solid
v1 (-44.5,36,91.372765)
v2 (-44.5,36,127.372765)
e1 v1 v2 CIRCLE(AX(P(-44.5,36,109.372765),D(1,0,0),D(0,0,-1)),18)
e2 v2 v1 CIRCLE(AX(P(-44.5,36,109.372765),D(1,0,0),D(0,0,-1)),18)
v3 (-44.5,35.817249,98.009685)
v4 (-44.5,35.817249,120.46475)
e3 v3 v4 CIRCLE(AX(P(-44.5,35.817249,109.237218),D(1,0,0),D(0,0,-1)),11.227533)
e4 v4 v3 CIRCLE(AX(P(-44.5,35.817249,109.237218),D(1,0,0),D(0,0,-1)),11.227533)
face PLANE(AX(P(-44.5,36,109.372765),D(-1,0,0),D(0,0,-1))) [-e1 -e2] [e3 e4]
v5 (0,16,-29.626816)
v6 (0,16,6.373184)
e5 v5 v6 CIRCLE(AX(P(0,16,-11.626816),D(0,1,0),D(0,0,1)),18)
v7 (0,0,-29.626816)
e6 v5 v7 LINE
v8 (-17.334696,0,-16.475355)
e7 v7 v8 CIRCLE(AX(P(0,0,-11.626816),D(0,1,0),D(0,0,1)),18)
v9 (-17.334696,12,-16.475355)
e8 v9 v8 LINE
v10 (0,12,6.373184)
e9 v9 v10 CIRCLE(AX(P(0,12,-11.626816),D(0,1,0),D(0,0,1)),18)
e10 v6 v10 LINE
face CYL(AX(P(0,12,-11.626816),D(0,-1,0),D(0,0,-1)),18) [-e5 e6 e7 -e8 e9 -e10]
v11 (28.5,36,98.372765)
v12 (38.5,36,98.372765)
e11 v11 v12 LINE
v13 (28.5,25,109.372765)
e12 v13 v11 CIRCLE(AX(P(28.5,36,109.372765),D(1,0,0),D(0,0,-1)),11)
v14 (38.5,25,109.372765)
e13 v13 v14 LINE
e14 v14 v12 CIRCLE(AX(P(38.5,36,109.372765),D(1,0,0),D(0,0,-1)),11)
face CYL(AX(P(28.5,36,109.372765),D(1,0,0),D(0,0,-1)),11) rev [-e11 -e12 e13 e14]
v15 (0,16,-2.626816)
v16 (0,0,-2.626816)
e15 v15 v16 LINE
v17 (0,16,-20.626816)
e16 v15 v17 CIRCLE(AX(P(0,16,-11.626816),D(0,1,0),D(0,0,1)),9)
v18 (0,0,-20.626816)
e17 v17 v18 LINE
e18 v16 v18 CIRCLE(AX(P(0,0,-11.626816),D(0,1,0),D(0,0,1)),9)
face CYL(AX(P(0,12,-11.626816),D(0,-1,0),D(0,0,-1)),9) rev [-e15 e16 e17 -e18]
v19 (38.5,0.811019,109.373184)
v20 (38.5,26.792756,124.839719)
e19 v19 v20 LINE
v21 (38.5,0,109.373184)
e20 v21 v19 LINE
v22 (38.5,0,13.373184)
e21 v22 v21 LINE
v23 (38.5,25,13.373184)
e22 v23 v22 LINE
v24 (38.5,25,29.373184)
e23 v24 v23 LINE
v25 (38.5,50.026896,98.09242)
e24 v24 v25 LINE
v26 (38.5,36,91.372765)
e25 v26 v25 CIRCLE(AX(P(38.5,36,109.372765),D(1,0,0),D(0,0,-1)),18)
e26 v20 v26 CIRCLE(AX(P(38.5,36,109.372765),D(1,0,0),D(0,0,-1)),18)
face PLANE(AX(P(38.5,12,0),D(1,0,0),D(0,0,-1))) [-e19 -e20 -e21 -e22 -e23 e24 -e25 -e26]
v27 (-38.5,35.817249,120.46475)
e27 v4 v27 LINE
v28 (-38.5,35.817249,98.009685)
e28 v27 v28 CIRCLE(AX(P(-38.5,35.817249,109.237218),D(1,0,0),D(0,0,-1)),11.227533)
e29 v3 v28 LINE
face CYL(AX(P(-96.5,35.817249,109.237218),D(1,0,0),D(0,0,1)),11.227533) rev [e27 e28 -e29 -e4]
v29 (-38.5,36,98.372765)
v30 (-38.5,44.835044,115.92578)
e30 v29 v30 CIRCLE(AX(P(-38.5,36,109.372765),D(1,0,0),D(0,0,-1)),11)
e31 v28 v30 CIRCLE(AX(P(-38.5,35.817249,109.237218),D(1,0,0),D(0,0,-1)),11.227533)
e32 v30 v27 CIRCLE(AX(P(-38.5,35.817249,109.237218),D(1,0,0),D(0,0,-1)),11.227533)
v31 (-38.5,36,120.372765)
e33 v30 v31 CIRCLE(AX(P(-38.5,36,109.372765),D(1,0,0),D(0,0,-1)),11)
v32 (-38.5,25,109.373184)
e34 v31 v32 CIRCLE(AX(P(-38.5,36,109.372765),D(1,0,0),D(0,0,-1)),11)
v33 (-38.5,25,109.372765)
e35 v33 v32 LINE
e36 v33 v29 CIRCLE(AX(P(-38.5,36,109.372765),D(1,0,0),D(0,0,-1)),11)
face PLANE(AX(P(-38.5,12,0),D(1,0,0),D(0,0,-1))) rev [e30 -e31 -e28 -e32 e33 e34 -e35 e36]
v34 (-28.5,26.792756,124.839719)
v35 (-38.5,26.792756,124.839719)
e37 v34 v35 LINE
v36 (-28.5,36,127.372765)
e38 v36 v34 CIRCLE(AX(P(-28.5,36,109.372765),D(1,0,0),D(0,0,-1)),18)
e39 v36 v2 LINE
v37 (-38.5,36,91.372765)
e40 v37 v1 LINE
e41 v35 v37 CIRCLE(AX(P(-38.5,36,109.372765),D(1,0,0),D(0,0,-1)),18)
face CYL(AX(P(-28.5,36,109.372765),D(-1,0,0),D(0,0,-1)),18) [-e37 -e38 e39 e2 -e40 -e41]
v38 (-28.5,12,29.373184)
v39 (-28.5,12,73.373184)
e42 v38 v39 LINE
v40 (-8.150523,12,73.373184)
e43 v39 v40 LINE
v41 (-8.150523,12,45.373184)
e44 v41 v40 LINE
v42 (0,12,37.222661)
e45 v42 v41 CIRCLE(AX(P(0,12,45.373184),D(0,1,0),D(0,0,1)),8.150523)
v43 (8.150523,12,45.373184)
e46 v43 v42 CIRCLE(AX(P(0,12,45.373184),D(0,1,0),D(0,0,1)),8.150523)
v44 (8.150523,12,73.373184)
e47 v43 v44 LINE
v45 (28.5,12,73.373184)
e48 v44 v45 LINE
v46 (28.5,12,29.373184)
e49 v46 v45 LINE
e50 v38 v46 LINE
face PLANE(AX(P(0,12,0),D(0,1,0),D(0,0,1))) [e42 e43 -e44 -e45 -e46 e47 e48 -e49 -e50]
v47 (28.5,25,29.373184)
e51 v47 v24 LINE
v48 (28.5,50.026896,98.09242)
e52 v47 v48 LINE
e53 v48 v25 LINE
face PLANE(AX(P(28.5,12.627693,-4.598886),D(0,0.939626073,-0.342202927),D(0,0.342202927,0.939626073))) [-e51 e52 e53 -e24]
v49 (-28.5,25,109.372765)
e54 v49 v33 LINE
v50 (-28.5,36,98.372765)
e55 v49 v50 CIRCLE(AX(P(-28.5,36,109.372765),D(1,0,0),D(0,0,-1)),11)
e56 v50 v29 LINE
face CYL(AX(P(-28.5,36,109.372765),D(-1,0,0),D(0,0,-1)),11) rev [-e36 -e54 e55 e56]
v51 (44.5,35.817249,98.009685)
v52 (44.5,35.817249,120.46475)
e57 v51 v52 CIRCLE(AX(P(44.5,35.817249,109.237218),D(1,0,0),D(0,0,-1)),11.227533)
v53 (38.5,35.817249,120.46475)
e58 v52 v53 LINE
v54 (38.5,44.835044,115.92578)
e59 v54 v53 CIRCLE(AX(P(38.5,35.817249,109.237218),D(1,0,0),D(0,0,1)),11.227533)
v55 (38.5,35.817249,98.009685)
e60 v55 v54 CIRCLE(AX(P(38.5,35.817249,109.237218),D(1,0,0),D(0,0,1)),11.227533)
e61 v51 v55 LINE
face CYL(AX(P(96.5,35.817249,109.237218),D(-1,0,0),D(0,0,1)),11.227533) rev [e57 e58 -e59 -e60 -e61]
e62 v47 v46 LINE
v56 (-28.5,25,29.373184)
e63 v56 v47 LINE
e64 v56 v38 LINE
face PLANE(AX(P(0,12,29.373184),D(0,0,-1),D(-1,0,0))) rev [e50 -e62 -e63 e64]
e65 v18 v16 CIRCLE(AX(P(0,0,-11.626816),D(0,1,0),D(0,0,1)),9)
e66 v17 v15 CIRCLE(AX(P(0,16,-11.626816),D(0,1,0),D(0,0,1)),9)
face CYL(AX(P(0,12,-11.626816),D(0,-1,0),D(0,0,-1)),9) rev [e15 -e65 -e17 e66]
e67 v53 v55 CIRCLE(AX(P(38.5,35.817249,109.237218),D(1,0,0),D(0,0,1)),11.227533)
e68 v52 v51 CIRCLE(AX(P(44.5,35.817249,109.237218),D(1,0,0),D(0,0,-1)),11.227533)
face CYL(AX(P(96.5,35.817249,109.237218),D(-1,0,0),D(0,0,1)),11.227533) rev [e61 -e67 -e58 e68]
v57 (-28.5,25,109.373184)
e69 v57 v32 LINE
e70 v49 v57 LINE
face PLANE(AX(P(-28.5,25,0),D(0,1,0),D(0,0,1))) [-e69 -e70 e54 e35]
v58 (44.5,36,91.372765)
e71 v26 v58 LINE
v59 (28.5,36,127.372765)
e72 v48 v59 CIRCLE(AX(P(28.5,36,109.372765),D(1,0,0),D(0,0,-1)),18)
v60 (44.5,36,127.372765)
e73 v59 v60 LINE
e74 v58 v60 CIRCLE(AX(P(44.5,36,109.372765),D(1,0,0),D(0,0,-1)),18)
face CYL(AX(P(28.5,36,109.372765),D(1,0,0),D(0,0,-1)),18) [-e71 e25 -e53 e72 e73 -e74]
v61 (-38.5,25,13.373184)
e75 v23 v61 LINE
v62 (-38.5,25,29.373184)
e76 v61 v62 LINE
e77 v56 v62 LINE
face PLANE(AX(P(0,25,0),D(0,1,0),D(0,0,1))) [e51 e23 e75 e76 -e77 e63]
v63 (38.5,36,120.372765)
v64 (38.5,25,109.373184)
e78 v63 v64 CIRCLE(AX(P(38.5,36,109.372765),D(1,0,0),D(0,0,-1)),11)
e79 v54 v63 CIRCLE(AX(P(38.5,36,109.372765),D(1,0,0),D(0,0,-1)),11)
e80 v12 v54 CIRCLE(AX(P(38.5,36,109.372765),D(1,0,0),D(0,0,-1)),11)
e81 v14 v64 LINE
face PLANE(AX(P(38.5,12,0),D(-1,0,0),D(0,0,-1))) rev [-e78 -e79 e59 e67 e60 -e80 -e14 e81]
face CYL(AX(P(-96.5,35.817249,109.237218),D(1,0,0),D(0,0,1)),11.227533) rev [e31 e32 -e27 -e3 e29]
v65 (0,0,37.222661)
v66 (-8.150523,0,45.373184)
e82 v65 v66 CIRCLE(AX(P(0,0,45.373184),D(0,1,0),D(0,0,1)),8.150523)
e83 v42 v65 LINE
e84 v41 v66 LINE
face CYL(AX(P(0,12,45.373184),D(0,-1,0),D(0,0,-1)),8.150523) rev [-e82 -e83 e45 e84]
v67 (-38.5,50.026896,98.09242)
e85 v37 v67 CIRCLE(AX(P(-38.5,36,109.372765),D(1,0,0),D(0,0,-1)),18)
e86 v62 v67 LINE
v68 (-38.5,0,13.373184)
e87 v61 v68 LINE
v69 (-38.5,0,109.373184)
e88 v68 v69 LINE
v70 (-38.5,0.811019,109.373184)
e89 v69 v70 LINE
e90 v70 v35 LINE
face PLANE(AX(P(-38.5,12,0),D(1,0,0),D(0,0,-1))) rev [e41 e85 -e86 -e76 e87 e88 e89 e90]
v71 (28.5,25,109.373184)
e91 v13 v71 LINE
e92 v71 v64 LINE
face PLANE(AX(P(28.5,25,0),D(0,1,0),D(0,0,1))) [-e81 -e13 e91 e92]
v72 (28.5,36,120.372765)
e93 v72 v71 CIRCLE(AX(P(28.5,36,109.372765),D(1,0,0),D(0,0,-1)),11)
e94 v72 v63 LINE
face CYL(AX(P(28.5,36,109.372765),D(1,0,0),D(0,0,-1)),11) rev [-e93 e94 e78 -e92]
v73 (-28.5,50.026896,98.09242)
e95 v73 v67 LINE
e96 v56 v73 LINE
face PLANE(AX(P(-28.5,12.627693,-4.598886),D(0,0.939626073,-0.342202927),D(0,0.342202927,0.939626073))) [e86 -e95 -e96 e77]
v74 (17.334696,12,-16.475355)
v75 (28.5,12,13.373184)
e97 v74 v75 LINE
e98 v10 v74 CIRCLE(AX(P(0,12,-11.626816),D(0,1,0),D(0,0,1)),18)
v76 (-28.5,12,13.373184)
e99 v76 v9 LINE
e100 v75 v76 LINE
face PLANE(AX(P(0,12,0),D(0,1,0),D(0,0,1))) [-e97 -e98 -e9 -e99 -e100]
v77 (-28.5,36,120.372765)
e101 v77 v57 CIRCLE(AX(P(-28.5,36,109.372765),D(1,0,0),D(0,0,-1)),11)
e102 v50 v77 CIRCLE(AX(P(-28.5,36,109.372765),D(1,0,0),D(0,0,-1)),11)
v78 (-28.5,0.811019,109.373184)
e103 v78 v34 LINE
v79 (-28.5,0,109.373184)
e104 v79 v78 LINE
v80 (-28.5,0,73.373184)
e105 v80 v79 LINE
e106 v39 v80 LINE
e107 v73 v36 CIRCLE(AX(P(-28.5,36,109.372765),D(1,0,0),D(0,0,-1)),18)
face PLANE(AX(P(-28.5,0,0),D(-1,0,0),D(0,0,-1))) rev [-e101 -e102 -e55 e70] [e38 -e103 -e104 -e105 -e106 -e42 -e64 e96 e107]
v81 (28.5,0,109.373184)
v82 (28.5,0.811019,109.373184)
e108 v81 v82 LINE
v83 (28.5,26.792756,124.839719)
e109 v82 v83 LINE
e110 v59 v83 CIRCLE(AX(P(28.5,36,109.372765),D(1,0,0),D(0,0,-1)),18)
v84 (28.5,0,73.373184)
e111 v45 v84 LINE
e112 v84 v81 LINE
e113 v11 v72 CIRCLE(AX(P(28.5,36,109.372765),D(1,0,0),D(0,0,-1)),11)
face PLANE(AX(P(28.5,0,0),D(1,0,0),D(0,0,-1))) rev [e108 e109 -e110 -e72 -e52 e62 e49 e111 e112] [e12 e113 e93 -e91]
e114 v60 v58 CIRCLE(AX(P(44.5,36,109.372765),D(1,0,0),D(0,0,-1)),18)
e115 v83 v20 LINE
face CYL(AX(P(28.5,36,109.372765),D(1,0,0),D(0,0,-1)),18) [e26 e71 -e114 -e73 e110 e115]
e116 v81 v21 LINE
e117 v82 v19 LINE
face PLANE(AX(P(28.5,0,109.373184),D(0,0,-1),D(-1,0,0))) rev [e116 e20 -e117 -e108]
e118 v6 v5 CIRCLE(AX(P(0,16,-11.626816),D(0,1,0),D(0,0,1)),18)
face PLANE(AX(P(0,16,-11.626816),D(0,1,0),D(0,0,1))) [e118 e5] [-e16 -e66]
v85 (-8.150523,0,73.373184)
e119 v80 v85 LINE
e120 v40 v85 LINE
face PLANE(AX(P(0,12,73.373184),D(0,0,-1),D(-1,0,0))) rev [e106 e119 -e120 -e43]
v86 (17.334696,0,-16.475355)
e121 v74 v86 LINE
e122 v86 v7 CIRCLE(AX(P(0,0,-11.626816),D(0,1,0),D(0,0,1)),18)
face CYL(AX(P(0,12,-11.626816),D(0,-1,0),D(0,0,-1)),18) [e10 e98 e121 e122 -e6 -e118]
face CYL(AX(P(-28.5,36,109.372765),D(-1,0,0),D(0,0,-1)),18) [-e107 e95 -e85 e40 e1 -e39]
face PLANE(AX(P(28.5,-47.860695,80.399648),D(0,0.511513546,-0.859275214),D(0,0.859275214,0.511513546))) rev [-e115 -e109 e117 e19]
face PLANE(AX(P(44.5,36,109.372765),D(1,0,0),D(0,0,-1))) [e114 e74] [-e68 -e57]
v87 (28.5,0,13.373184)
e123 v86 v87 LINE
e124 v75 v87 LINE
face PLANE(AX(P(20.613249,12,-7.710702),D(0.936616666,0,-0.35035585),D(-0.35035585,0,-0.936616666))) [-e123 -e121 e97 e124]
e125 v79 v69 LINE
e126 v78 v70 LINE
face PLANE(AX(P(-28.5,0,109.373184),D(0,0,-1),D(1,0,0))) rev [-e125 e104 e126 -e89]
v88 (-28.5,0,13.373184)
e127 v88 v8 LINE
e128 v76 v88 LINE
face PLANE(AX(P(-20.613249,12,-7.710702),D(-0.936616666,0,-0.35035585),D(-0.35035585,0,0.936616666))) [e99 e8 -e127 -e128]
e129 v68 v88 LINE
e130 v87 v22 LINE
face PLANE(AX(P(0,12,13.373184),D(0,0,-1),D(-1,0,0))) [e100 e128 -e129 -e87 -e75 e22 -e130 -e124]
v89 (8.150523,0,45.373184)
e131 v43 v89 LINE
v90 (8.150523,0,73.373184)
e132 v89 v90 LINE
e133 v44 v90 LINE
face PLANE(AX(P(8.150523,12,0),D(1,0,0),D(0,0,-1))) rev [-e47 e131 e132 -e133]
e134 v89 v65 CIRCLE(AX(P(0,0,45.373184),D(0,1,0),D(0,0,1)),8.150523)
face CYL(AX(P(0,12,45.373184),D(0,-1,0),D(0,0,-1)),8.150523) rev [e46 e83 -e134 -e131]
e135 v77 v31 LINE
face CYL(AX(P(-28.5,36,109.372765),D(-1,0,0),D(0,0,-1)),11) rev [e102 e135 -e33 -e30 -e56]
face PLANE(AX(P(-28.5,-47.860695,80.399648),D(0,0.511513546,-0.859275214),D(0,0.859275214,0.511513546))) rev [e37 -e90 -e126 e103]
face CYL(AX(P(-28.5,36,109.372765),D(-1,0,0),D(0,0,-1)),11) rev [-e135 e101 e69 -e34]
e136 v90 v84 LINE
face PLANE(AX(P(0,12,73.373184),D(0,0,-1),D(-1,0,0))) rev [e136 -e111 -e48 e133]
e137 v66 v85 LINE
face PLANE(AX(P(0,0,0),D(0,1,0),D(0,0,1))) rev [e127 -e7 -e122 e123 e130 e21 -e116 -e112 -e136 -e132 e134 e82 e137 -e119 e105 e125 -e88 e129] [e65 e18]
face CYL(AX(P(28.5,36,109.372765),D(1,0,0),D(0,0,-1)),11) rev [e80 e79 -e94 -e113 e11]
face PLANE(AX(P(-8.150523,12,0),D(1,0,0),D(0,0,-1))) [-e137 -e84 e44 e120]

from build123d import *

# Parameters (mm, degrees)
BASE_PLATE_SKETCH_R   = 18
BASE_PLATE_SKETCH_R_2 = 9
BASE_PLATE_DEPTH      = 12
CENTRE_BLOCK_SKETCH_W = 77
CENTRE_BLOCK_SKETCH_H = 16
CENTRE_BLOCK_DEPTH    = 13
CLEVIS_ARM_DEPTH      = 10
EYE_HUB_SKETCH_R      = 18
EYE_HUB_BOSS_DEPTH    = 6
PIVOT_BORE_SKETCH_R   = 11.227532681
PIVOT_BORE_DEPTH      = 68
BASE_BOSS_SKETCH_R    = 18
BASE_BOSS_SKETCH_R_2  = 9
BASE_BOSS_4MM_DEPTH   = 4


with BuildPart() as part:
    # Base Plate Sketch → Base Plate (new body)
    # profile 1 of 4: a face of its own
    with BuildSketch(Plane(origin=(0, 0, 0), x_dir=(1, 0, 0), z_dir=(0, 1, 0))):
        with BuildLine():
            ThreePointArc((8.150523058, -45.373183795), (0, -37.222660737), (-8.150523058, -45.373183795))
            Line((-8.150523058, -45.373183795), (-8.150523058, -73.373183795))
            Line((-8.150523058, -73.373183795), (-28.5, -73.373183795))
            Line((-28.5, -73.373183795), (-28.5, -29.373183795))
            Line((-28.5, -29.373183795), (28.5, -29.373183795))
            Line((28.5, -29.373183795), (28.5, -73.373183795))
            Line((28.5, -73.373183795), (8.150523058, -73.373183795))
            Line((8.150523058, -73.373183795), (8.150523058, -45.373183795))
        make_face()
    # profile 2 of 4: a face of its own
    with BuildSketch(Plane(origin=(0, 0, 0), x_dir=(1, 0, 0), z_dir=(0, 1, 0))):
        Polygon((28.5, -13.373183795), (0, -13.373183795), (-28.5, -13.373183795), (-38.5, -13.373183795), (-38.5, -29.373183795), (-28.5, -29.373183795), (28.5, -29.373183795), (38.5, -29.373183795), (38.5, -13.373183795), align=None)
    # profile 3 of 4: a face of its own
    with BuildSketch(Plane(origin=(0, 0, 0), x_dir=(1, 0, 0), z_dir=(0, 1, 0))):
        with BuildLine():
            Line((-28.5, -13.373183795), (0, -13.373183795))
            Line((0, -13.373183795), (28.5, -13.373183795))
            Line((28.5, -13.373183795), (17.334695629, 16.475354899))
            ThreePointArc((17.334695629, 16.475354899), (17.832898269, 14.073801972), (18, 11.626816205))
            ThreePointArc((18, 11.626816205), (-2.446985767, -6.206082063), (-17.334695629, 16.475354899))
            Line((-17.334695629, 16.475354899), (-28.5, -13.373183795))
        make_face()
    # profile 4 of 4: a face of its own
    with BuildSketch(Plane(origin=(0, 0, 0), x_dir=(1, 0, 0), z_dir=(0, 1, 0))):
        with Locations((0, 11.626816205)):
            Circle(BASE_PLATE_SKETCH_R)
        with Locations(Location((0, 11.626816205, 0), (0, 0, 270))):
            Circle(BASE_PLATE_SKETCH_R_2, mode=Mode.SUBTRACT)
    extrude(amount=BASE_PLATE_DEPTH)

    # Centre Block Sketch → Centre Block (add)
    with BuildSketch(Plane(origin=(0, 12, 0), x_dir=(1, 0, 0), z_dir=(0, 1, 0))):
        with Locations((0, -21.373183795)):
            Rectangle(CENTRE_BLOCK_SKETCH_W, CENTRE_BLOCK_SKETCH_H)
    extrude(amount=CENTRE_BLOCK_DEPTH)

    # Clevis Arm Sketch → Clevis Arm (add)
    # profile 1 of 2: a face of its own
    with BuildSketch(Plane(origin=(38.5, 0, 0), x_dir=(0, 0, -1), z_dir=(1, 0, 0))):
        with BuildLine():
            Line((-29.373183795, 0), (-29.373183795, 24.999999998))
            Line((-29.373183795, 24.999999998), (-98.092419727, 50.026895655))
            ThreePointArc((-98.092419726, 50.026895656), (-93.139370455, 43.776688822), (-91.372765384, 35.999999998))
            ThreePointArc((-91.372765384, 35.999999998), (-104.59810148, 18.644811016), (-124.839719228, 26.792756176))
            Line((-124.839719228, 26.792756176), (-109.373183795, 0.811018934))
            Line((-109.373183795, 0.811018934), (-109.373183795, 0))
            Line((-109.373183795, 0), (-29.373183795, 0))
        make_face()
    # profile 2 of 2: a face of its own
    with BuildSketch(Plane(origin=(38.5, 0, 0), x_dir=(0, 0, -1), z_dir=(1, 0, 0))):
        with BuildLine():
            ThreePointArc((-91.372765384, 35.999999998), (-93.139370455, 43.776688822), (-98.092419726, 50.026895656))
            ThreePointArc((-98.092419726, 50.026895656), (-121.176926997, 49.589031186), (-124.839719228, 26.792756176))
            ThreePointArc((-124.839719228, 26.792756176), (-104.59810148, 18.644811016), (-91.372765384, 35.999999998))
        make_face()
        with BuildLine():
            ThreePointArc((-98.372765384, 35.999999998), (-101.594590791, 28.221825405), (-109.372765384, 24.999999998))
            Line((-109.372765384, 24.999999998), (-109.373183795, 24.999999998))
            ThreePointArc((-109.373183795, 25.000000006), (-117.150792046, 43.77832252), (-98.372765384, 35.999999998))
        make_face(mode=Mode.SUBTRACT)
    extrude(amount=-CLEVIS_ARM_DEPTH)

    # Clevis Arm Mirror: part across plane


with BuildPart() as part_1:
    add(part.part)
    add(part.part.mirror(Plane(origin=(0, 0, 0), x_dir=(0, 0, 1), z_dir=(1, 0, 0))))

    # Eye Hub Sketch → Eye Hub Boss (add)
    with BuildSketch(Plane(origin=(38.5, 0, 0), x_dir=(0, 0, -1), z_dir=(1, 0, 0))):
        with Locations((-109.372765384, 35.999999998)):
            Circle(EYE_HUB_SKETCH_R)
    extrude(amount=EYE_HUB_BOSS_DEPTH)

    # Pivot Bore Sketch → Pivot Bore (cut)
    with BuildSketch(Plane.ZY.offset(-28.5)):
        with Locations((109.237217655, 35.817248986)):
            Circle(PIVOT_BORE_SKETCH_R)
    extrude(amount=-PIVOT_BORE_DEPTH, mode=Mode.SUBTRACT)

    # Eye Hub and Bore Mirror: part across plane


with BuildPart() as part_2:
    add(part_1.part)
    add(part_1.part.mirror(Plane(origin=(0, 0, 0), x_dir=(0, 0, 1), z_dir=(1, 0, 0))))

    # Base Boss Sketch → Base Boss 4mm (add)
    with BuildSketch(Plane(origin=(0, 12, 0), x_dir=(1, 0, 0), z_dir=(0, 1, 0))):
        with Locations(Location((0, 11.626816205, 0), (0, 0, 164.373619322))):
            Circle(BASE_BOSS_SKETCH_R)
        with Locations(Location((0, 11.626816205, 0), (0, 0, 270))):
            Circle(BASE_BOSS_SKETCH_R_2, mode=Mode.SUBTRACT)
    extrude(amount=BASE_BOSS_4MM_DEPTH)


solid = part_2.part
